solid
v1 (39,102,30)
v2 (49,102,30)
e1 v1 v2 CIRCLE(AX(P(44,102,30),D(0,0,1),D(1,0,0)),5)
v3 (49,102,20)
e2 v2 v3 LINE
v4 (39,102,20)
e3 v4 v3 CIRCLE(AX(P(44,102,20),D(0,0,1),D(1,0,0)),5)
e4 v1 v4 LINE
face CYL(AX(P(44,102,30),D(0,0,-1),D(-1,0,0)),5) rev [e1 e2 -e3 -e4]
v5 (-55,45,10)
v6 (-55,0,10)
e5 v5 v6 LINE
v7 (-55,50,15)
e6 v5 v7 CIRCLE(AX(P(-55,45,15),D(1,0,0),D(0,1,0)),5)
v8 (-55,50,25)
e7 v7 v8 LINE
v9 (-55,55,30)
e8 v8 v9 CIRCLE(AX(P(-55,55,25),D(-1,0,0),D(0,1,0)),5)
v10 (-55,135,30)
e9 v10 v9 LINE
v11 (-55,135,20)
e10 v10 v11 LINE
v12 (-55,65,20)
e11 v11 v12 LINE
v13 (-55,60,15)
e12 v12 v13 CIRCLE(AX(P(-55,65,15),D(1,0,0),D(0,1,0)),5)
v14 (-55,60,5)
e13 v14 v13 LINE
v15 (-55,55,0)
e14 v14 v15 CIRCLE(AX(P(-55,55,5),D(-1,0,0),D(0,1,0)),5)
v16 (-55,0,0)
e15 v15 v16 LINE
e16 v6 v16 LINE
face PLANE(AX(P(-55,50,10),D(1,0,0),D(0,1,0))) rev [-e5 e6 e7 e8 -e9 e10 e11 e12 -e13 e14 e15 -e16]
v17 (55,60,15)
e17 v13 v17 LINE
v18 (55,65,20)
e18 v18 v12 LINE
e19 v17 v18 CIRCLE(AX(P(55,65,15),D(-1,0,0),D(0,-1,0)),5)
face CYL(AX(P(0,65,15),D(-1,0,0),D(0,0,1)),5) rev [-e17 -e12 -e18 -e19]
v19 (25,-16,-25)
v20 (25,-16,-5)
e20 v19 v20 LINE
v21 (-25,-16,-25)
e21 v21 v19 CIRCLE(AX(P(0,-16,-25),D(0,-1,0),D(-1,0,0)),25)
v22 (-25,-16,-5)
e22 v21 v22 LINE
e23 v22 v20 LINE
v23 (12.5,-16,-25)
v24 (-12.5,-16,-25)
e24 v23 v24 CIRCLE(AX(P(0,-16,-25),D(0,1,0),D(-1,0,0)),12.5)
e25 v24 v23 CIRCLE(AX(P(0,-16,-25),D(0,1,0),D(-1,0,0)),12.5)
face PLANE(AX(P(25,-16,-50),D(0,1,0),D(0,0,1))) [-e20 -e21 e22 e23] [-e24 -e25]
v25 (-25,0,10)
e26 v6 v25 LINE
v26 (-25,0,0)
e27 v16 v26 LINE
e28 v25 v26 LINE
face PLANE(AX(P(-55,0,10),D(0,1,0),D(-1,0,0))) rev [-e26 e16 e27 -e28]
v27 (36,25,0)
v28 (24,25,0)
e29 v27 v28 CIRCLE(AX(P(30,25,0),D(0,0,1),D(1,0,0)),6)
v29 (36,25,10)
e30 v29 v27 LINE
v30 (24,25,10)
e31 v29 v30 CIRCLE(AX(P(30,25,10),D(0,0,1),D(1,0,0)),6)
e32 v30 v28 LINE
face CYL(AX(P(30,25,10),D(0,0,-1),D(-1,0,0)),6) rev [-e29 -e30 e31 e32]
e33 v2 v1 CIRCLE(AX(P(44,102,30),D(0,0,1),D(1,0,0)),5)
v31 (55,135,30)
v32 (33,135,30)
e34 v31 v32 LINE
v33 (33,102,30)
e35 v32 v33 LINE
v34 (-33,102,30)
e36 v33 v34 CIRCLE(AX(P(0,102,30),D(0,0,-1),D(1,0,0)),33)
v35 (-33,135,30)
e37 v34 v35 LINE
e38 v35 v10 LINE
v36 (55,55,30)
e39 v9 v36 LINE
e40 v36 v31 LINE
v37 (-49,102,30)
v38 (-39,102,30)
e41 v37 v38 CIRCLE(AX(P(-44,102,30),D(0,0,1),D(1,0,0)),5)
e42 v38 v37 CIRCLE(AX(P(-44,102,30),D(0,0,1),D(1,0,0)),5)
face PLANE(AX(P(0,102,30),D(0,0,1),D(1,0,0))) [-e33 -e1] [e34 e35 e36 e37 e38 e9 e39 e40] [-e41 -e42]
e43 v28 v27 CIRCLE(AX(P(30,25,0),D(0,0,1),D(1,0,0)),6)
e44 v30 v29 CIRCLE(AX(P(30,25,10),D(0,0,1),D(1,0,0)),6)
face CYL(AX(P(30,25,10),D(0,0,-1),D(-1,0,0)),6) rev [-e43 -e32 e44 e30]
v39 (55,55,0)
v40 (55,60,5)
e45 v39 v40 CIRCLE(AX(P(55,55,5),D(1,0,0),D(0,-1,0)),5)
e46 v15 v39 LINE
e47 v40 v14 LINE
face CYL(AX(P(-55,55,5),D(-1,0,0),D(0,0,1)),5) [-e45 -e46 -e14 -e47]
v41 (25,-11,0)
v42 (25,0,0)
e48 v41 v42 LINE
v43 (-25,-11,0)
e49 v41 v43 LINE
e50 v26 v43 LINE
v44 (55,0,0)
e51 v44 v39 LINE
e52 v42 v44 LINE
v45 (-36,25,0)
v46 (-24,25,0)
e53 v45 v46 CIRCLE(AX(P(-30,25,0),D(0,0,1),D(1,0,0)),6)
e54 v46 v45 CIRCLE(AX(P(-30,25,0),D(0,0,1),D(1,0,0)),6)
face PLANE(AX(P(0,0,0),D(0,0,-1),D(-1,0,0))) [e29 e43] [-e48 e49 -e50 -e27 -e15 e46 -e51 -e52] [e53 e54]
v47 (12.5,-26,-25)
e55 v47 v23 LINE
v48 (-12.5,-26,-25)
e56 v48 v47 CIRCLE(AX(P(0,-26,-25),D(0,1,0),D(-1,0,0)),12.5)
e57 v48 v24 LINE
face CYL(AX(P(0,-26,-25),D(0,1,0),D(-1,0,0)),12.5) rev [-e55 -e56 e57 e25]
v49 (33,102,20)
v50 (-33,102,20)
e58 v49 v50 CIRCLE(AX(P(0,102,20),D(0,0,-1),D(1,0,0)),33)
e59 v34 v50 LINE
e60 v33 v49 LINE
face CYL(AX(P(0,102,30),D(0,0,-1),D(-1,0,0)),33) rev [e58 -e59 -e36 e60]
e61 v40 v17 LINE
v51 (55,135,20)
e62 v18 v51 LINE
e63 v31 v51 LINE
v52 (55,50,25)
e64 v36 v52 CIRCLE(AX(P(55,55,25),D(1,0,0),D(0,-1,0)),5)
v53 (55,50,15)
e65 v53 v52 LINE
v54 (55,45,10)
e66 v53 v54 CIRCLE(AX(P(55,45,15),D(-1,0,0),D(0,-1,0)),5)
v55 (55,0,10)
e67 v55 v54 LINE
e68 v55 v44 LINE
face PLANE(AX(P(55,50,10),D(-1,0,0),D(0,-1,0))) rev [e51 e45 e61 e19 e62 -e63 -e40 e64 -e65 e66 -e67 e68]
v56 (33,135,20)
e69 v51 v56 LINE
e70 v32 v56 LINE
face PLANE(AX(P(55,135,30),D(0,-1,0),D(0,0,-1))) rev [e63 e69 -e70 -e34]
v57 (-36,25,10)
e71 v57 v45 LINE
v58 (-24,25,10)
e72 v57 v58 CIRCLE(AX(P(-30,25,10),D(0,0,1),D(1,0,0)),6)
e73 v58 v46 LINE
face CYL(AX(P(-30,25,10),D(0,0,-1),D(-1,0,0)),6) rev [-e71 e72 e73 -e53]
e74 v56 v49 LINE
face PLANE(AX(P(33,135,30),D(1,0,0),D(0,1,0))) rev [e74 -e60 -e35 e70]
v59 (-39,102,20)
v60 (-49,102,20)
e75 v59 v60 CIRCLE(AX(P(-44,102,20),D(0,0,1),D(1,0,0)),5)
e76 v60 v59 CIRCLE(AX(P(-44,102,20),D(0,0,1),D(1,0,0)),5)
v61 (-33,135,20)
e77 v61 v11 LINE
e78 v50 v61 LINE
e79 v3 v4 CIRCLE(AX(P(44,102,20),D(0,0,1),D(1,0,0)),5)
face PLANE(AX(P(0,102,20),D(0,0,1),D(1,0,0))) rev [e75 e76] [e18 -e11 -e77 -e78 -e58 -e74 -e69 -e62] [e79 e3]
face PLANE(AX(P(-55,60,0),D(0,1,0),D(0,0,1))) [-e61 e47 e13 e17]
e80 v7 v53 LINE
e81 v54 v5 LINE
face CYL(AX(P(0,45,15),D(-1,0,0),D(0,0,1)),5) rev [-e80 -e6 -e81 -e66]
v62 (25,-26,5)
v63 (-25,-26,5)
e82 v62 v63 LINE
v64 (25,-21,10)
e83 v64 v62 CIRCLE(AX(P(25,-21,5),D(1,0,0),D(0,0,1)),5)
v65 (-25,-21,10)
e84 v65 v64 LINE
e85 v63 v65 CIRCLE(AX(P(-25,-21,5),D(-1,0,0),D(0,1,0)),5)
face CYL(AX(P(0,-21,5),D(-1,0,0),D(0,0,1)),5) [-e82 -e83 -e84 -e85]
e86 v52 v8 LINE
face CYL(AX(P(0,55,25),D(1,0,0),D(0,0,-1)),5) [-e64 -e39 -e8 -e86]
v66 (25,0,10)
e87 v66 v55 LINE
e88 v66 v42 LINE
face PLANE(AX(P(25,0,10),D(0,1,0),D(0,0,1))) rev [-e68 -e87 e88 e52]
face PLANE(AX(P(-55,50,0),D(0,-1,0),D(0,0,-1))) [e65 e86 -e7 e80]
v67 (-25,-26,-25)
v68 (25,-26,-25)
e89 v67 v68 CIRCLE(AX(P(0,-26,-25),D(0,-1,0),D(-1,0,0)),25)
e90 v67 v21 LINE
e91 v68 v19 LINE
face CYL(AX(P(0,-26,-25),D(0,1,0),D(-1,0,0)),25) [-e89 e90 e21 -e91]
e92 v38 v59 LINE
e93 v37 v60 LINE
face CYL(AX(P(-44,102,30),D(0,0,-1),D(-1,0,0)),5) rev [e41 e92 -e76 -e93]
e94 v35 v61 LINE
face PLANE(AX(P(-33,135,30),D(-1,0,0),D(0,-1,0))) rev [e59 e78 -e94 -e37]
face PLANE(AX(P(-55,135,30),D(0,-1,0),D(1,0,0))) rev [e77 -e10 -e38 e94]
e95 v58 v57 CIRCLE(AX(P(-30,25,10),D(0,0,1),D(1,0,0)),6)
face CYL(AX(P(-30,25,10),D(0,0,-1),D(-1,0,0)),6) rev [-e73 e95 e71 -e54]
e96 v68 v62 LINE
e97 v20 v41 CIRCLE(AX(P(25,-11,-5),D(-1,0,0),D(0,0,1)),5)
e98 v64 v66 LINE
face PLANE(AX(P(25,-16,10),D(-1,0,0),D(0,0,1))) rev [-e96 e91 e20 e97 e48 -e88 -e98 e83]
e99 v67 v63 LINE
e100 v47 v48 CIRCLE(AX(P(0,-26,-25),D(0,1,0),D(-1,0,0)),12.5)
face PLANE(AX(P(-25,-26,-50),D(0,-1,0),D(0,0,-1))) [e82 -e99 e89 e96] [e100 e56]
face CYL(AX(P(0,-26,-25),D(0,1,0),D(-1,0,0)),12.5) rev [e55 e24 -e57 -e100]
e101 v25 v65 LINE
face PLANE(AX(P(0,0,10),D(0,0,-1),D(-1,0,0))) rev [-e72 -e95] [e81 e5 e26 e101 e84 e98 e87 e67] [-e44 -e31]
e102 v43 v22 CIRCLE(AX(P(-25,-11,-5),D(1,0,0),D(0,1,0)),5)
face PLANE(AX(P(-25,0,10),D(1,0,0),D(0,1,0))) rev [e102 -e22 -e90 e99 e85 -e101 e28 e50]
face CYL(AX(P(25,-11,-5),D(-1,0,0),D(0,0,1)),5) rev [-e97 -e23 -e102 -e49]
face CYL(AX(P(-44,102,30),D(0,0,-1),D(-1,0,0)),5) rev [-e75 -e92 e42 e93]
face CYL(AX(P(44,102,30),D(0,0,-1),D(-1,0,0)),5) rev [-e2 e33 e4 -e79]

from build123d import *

# Parameters (mm, degrees)
SKETCH_1_R           = 6
EXTRUDE_1_DEPTH      = 10
SKETCH_2_W           = 50
SKETCH_2_H           = 10
EXTRUDE_2_DEPTH      = 60
SKETCH_3_R           = 12.5
CUT_EXTRUDE_1_DEPTH  = 10
FILLET_1_R           = 5
EXTRUDE_3_DEPTH      = 10
EXTRUDE_3_DEPTH_BACK = 10
SKETCH_5_W           = 110
SKETCH_5_H           = 10
SKETCH_6_R           = 5
EXTRUDE_4_DEPTH      = 10
FILLET_2_R           = 5


with BuildPart() as part:
    # 草图1 → 凸台-拉伸1 (new body)
    with BuildSketch(Plane.XY):
        Polygon((-55, 50), (55, 50), (55, 0), (50, 0), (25, 0), (25, -16), (-25, -16), (-25, 0), (-55, 0), align=None)
        with Locations((-30, 25)):
            Circle(SKETCH_1_R, mode=Mode.SUBTRACT)
        with Locations((30, 25)):
            Circle(SKETCH_1_R, mode=Mode.SUBTRACT)
    extrude(amount=EXTRUDE_1_DEPTH)

    # 草图2 → 凸台-拉伸2 (add)
    with BuildSketch(Plane.XY.offset(10)):
        with Locations((0, -21)):
            Rectangle(SKETCH_2_W, SKETCH_2_H)
    extrude(amount=-EXTRUDE_2_DEPTH)

    # 草图3 → 切除-拉伸1 (cut)
    with BuildSketch(Plane(origin=(0, -16, 0), x_dir=(1, 0, 0), z_dir=(0, 1, 0))):
        with Locations(Location((0, 25, 0), (0, 0, 180))):
            Circle(SKETCH_3_R)
        with BuildLine():
            Line((-25, 25), (-25, 57.057636161))
            Line((-25, 57.057636161), (25, 57.057636161))
            Line((25, 57.057636161), (25, 25))
            ThreePointArc((25, 25), (0, 50), (-25, 25))
        make_face()
    extrude(amount=-CUT_EXTRUDE_1_DEPTH, mode=Mode.SUBTRACT)

    # 圆角1
    fillet_1_edges = [part.edges().sort_by_distance(p)[0] for p in [
        (0, -16, 0),
        (0, -26, 10),
    ]]
    fillet(fillet_1_edges, radius=FILLET_1_R)

    # 草图5 → 凸台-拉伸3 (add, two sides: drawn at the far end of the back side and taken through both)
    with BuildSketch(Plane.XY.offset(10).offset(-EXTRUDE_3_DEPTH_BACK)):
        with Locations((0, 55)):
            Rectangle(SKETCH_5_W, SKETCH_5_H)
    extrude(amount=EXTRUDE_3_DEPTH + EXTRUDE_3_DEPTH_BACK)

    # 草图6 → 凸台-拉伸4 (add)
    with BuildSketch(Plane.XY.offset(20)):
        with BuildLine():
            Line((-55, 60), (-55, 135))
            Line((-55, 135), (-33, 135))
            Line((-33, 135), (-33, 102))
            ThreePointArc((-33, 102), (0, 69), (33, 102))
            Line((33, 102), (33, 135))
            Line((33, 135), (55, 135))
            Line((55, 135), (55, 60))
            Line((55, 60), (55, 50))
            Line((55, 50), (-55, 50))
            Line((-55, 50), (-55, 60))
        make_face()
        with Locations((44, 102)):
            Circle(SKETCH_6_R, mode=Mode.SUBTRACT)
        with Locations((-44, 102)):
            Circle(SKETCH_6_R, mode=Mode.SUBTRACT)
    extrude(amount=EXTRUDE_4_DEPTH)

    # 圆角2
    fillet_2_edges = [part.edges().sort_by_distance(p)[0] for p in [
        (0, 50, 10),
        (0, 50, 30),
        (0, 60, 20),
        (0, 60, 0),
    ]]
    fillet(fillet_2_edges, radius=FILLET_2_R)


solid = part.part
